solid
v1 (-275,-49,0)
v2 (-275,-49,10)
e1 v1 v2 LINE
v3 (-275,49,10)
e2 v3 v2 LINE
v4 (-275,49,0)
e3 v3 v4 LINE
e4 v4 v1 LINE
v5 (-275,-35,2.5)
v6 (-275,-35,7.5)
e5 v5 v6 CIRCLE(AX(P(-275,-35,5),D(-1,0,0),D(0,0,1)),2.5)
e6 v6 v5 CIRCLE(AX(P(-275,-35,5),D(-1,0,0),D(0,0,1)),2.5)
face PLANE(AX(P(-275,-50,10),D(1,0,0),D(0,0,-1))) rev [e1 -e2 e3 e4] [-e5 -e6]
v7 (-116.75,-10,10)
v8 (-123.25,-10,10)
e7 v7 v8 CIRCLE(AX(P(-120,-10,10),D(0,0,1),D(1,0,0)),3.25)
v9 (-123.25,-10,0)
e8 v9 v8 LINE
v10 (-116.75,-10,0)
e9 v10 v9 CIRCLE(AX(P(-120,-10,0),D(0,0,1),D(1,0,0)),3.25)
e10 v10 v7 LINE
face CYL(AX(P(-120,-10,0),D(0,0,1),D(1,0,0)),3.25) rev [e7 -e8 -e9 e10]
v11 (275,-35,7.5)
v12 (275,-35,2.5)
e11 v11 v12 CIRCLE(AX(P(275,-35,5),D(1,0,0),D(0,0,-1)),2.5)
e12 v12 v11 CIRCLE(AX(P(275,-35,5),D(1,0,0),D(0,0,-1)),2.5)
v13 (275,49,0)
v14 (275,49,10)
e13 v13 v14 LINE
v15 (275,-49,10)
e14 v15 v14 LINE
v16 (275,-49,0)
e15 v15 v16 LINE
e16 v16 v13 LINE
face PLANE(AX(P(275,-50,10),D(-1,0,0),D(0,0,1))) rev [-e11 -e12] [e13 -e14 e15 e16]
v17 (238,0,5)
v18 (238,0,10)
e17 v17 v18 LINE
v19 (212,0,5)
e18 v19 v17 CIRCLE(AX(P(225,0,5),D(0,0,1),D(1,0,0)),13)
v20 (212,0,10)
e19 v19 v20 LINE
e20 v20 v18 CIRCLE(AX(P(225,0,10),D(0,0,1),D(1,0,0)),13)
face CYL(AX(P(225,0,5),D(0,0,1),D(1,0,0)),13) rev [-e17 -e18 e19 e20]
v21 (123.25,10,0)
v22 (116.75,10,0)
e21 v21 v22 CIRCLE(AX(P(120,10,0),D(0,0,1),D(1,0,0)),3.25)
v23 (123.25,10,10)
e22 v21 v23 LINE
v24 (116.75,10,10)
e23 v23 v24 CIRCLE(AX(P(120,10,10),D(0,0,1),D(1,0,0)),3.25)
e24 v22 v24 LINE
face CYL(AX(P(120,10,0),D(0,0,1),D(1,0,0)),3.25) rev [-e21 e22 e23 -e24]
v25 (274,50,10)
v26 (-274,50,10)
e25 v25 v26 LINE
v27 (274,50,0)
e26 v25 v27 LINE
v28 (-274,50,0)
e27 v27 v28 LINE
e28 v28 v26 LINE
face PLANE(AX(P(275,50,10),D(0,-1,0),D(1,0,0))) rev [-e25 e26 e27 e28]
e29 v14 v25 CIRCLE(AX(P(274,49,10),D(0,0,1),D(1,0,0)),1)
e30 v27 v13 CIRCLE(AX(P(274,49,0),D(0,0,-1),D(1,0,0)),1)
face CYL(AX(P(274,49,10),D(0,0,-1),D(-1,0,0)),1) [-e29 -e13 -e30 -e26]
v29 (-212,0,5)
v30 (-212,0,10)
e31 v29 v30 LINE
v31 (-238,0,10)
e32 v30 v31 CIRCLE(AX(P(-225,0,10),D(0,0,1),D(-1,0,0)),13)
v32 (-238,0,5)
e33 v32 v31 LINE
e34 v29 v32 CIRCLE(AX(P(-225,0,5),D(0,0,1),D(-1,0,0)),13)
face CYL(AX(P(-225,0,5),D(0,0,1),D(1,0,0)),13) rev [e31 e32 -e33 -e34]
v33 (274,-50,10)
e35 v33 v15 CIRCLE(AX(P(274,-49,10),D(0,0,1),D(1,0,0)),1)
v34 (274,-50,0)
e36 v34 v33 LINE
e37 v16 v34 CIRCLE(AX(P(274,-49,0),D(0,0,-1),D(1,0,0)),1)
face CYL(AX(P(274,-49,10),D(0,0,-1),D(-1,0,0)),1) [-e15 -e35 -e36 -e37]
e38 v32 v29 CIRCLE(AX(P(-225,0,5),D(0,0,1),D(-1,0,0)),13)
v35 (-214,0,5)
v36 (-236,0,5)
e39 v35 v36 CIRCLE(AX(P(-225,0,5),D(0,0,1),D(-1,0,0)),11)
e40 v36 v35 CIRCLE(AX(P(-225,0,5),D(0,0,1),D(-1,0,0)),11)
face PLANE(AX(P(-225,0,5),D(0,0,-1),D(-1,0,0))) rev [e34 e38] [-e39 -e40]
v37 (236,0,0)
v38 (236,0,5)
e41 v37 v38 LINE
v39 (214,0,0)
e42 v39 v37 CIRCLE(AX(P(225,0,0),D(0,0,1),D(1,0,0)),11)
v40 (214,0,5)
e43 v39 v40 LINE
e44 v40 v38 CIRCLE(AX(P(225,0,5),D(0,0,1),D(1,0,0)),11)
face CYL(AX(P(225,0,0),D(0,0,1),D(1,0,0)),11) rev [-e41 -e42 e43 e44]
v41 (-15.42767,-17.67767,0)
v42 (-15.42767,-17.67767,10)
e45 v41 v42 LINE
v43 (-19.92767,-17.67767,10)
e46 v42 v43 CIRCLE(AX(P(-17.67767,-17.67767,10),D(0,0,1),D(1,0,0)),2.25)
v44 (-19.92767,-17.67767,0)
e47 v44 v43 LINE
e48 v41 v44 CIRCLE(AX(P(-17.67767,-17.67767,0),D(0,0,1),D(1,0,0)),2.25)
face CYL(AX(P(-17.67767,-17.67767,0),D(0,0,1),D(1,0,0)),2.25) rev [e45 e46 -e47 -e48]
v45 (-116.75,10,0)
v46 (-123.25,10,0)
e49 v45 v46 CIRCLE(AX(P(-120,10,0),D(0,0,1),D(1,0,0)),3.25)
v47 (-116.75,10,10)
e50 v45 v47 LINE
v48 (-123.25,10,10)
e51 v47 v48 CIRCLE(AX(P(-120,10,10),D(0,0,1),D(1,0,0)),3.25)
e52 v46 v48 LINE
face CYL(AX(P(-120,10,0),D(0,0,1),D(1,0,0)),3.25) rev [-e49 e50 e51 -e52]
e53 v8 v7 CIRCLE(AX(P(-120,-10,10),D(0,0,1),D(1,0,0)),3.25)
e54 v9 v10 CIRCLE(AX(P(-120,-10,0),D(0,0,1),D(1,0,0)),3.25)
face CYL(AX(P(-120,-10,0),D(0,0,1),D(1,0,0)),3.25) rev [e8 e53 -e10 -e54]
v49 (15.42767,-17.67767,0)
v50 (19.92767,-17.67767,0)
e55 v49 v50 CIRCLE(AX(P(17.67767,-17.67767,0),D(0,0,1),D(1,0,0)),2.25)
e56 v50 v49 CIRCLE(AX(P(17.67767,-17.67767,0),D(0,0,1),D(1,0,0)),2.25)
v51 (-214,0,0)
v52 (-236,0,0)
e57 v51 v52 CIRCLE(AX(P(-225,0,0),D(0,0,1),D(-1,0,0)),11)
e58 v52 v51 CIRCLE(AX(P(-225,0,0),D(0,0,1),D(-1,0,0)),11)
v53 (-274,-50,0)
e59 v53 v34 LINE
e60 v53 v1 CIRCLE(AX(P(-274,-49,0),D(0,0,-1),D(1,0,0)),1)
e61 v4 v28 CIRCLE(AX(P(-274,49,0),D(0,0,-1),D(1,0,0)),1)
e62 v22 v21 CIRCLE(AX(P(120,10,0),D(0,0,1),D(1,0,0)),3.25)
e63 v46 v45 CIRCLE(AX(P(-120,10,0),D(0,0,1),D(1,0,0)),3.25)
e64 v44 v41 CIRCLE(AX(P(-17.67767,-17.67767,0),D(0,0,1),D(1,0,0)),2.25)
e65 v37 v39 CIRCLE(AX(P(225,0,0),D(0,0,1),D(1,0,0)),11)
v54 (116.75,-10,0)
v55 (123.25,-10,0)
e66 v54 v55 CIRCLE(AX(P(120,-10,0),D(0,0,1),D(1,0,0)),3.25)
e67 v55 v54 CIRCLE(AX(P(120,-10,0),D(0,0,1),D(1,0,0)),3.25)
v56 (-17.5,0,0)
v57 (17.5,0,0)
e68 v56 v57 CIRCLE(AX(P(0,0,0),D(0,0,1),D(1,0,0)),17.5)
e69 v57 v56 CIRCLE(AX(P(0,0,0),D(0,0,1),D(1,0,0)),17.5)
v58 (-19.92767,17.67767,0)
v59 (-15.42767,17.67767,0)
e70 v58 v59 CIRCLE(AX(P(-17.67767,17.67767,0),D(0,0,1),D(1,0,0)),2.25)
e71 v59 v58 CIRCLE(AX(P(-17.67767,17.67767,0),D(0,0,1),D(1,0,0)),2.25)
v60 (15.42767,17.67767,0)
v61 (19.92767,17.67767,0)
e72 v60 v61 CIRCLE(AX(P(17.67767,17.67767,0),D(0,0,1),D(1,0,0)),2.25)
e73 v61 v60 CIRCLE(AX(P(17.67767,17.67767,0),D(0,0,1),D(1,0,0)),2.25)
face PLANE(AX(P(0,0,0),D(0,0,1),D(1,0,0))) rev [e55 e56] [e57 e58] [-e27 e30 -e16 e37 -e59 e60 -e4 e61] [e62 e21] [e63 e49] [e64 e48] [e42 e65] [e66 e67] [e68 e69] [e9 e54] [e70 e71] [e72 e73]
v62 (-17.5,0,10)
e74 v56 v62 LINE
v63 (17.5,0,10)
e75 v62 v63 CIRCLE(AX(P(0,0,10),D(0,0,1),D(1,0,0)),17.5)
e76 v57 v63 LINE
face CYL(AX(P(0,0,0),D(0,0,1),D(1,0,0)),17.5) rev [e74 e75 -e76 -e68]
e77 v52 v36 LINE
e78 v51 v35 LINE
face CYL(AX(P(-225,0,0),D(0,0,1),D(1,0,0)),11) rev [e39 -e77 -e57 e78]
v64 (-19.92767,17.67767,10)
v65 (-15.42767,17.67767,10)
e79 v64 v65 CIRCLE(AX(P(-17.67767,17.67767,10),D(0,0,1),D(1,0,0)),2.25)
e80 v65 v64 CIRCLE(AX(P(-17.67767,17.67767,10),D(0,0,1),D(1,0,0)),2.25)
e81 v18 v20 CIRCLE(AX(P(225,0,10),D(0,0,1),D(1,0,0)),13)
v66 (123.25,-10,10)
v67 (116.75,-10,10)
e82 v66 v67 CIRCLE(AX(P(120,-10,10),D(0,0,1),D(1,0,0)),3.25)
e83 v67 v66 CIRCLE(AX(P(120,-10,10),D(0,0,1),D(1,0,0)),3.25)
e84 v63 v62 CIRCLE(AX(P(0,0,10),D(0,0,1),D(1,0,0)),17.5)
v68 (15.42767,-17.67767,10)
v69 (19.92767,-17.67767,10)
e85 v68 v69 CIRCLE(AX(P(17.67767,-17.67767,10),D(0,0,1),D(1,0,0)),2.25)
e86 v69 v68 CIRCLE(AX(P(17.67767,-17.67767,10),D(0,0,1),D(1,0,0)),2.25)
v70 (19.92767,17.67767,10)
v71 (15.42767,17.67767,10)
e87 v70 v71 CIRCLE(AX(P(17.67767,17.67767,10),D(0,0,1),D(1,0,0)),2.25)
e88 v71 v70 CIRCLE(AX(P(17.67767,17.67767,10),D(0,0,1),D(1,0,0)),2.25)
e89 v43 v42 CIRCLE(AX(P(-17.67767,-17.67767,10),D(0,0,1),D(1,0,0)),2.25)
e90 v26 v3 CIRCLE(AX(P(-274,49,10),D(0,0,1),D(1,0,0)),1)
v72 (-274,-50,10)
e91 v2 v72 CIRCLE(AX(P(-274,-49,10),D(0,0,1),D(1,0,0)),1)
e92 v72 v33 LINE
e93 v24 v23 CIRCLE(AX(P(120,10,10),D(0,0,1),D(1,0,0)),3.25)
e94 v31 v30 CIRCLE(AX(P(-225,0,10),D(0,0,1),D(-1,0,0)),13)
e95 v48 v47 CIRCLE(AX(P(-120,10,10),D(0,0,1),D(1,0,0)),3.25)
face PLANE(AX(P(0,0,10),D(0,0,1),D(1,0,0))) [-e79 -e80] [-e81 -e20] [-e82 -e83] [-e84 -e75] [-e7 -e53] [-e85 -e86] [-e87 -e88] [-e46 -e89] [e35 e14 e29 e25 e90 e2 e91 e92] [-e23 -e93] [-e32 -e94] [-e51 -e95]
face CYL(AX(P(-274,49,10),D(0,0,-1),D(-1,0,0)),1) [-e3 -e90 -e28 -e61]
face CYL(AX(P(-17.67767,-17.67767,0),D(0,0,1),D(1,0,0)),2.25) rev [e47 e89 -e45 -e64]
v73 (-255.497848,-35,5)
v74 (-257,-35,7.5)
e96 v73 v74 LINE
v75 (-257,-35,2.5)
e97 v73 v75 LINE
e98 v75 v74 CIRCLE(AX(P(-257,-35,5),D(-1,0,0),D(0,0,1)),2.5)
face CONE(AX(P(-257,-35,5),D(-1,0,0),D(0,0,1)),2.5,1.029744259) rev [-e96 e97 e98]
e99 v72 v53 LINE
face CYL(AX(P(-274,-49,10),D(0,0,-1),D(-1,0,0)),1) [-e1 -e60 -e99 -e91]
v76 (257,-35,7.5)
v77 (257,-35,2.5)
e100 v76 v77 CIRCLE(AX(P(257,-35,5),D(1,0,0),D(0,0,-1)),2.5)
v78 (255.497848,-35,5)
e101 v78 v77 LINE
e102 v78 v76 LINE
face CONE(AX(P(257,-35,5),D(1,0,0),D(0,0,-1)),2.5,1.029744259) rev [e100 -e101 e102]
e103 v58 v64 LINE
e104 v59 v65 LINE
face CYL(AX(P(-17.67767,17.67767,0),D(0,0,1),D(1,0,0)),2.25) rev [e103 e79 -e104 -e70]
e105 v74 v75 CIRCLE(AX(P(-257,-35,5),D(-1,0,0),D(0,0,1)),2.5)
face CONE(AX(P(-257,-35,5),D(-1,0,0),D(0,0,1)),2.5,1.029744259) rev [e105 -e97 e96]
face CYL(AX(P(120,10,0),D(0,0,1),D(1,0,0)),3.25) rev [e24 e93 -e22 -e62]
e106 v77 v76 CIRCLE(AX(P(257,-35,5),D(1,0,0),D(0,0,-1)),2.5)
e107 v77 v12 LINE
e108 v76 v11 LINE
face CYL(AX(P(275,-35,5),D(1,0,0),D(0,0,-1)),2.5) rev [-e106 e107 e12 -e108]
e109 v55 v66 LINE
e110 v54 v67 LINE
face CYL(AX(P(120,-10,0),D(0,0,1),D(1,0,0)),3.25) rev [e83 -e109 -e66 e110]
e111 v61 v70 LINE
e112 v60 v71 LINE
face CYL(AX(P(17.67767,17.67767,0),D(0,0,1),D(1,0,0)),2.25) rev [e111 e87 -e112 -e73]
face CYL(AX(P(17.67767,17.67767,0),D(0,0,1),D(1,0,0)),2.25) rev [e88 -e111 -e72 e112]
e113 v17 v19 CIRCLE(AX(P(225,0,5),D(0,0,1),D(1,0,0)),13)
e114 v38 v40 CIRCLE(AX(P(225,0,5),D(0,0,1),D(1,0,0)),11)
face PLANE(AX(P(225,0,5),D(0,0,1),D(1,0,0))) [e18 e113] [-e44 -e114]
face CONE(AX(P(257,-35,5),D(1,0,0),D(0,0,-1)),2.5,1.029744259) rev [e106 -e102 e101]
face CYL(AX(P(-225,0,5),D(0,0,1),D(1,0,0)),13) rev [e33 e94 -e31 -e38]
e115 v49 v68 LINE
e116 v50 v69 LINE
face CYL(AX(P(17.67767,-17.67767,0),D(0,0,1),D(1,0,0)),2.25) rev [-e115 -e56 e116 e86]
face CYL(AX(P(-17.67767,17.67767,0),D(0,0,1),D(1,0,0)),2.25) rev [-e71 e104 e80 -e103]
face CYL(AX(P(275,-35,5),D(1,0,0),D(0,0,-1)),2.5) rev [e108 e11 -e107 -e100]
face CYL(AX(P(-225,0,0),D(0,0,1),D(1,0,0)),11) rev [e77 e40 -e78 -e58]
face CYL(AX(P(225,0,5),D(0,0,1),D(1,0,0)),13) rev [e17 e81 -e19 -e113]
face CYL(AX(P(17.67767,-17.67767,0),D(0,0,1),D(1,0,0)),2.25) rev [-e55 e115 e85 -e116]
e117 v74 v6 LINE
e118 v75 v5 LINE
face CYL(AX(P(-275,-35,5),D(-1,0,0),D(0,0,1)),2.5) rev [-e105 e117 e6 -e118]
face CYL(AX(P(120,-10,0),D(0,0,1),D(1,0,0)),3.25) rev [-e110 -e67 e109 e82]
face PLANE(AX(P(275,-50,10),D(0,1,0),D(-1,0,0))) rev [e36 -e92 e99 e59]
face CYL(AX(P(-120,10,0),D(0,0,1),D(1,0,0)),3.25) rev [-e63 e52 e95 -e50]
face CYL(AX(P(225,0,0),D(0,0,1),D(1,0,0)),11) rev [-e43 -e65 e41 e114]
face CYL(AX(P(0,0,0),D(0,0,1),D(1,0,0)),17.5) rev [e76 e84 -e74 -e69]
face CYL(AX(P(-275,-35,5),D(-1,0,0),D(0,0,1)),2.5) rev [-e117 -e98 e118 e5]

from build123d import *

# Parameters (mm, degrees)
SKETCH1_W           = 550
SKETCH1_H           = 100
BOSS_EXTRUDE1_DEPTH = 10
SKETCH3_R           = 13
CUT_EXTRUDE2_DEPTH  = 5
SKETCH4_R           = 11
CUT_EXTRUDE3_DEPTH  = 280.55321497
SKETCH5_R           = 17.5
CUT_EXTRUDE4_DEPTH  = 280.687325419
SKETCH6_R           = 2.25
CUT_EXTRUDE5_DEPTH  = 280.687325419
SKETCH7_R           = 3.25
CUT_EXTRUDE6_DEPTH  = 280.687325419
FILLET1_R           = 1


with BuildPart() as part:
    # Sketch1 → Boss-Extrude1 (new body)
    with BuildSketch(Plane.XY):
        Rectangle(SKETCH1_W, SKETCH1_H)
    extrude(amount=BOSS_EXTRUDE1_DEPTH)

    # Sketch3 → Cut-Extrude2 (cut)
    with BuildSketch(Plane.XY.offset(10)):
        with Locations((225, 0)):
            Circle(SKETCH3_R)
        with Locations(Location((-225, 0, 0), (0, 0, 180))):
            Circle(SKETCH3_R)
    extrude(amount=-CUT_EXTRUDE2_DEPTH, mode=Mode.SUBTRACT)

    # Sketch4 → Cut-Extrude3 (cut, through all)
    with BuildSketch(Plane.XY.offset(5)):
        with Locations((225, 0)):
            Circle(SKETCH4_R)
        with Locations(Location((-225, 0, 0), (0, 0, 180))):
            Circle(SKETCH4_R)
    extrude(amount=-CUT_EXTRUDE3_DEPTH, mode=Mode.SUBTRACT)

    # Sketch5 → Cut-Extrude4 (cut, through all)
    with BuildSketch(Plane.XY.offset(10)):
        Circle(SKETCH5_R)
    extrude(amount=-CUT_EXTRUDE4_DEPTH, mode=Mode.SUBTRACT)

    # Sketch6 → Cut-Extrude5 (cut, through all)
    with BuildSketch(Plane.XY.offset(10)):
        with Locations((-17.67766953, 17.67766953)):
            Circle(SKETCH6_R)
        with Locations((17.67766953, 17.67766953)):
            Circle(SKETCH6_R)
        with Locations((17.67766953, -17.67766953)):
            Circle(SKETCH6_R)
        with Locations((-17.67766953, -17.67766953)):
            Circle(SKETCH6_R)
    extrude(amount=-CUT_EXTRUDE5_DEPTH, mode=Mode.SUBTRACT)

    # Sketch7 → Cut-Extrude6 (cut, through all)
    with BuildSketch(Plane.XY.offset(10)):
        with Locations((-120, -10)):
            Circle(SKETCH7_R)
        with Locations((120, -10)):
            Circle(SKETCH7_R)
        with Locations((120, 10)):
            Circle(SKETCH7_R)
        with Locations((-120, 10)):
            Circle(SKETCH7_R)
    extrude(amount=-CUT_EXTRUDE6_DEPTH, mode=Mode.SUBTRACT)

    # Fillet1
    fillet1_edges = [part.edges().sort_by_distance(p)[0] for p in [
        (-275, 50, 5),
        (275, 50, 5),
        (275, -50, 5),
        (-275, -50, 5),
    ]]
    fillet(fillet1_edges, radius=FILLET1_R)

    # Sketch9 → M6 Tapped Hole1 (revolve, cut)
    with BuildSketch(Plane(origin=(-275, -35, 5), x_dir=(0, 0, 1), z_dir=(0, 1, 0))):
        Polygon((0, 0), (0, 19.502151548), (2.5, 18), (2.5, 0), align=None)
    m6_tapped_hole1 = revolve(axis=Axis((-281.35, -35, 5), (1, 0, 0)), mode=Mode.SUBTRACT)

    # Mirror1: M6 Tapped Hole1 across plane
    add(m6_tapped_hole1.mirror(Plane(origin=(0, 0, 0), x_dir=(0, 0, 1), z_dir=(1, 0, 0))), mode=Mode.SUBTRACT)


solid = part.part
